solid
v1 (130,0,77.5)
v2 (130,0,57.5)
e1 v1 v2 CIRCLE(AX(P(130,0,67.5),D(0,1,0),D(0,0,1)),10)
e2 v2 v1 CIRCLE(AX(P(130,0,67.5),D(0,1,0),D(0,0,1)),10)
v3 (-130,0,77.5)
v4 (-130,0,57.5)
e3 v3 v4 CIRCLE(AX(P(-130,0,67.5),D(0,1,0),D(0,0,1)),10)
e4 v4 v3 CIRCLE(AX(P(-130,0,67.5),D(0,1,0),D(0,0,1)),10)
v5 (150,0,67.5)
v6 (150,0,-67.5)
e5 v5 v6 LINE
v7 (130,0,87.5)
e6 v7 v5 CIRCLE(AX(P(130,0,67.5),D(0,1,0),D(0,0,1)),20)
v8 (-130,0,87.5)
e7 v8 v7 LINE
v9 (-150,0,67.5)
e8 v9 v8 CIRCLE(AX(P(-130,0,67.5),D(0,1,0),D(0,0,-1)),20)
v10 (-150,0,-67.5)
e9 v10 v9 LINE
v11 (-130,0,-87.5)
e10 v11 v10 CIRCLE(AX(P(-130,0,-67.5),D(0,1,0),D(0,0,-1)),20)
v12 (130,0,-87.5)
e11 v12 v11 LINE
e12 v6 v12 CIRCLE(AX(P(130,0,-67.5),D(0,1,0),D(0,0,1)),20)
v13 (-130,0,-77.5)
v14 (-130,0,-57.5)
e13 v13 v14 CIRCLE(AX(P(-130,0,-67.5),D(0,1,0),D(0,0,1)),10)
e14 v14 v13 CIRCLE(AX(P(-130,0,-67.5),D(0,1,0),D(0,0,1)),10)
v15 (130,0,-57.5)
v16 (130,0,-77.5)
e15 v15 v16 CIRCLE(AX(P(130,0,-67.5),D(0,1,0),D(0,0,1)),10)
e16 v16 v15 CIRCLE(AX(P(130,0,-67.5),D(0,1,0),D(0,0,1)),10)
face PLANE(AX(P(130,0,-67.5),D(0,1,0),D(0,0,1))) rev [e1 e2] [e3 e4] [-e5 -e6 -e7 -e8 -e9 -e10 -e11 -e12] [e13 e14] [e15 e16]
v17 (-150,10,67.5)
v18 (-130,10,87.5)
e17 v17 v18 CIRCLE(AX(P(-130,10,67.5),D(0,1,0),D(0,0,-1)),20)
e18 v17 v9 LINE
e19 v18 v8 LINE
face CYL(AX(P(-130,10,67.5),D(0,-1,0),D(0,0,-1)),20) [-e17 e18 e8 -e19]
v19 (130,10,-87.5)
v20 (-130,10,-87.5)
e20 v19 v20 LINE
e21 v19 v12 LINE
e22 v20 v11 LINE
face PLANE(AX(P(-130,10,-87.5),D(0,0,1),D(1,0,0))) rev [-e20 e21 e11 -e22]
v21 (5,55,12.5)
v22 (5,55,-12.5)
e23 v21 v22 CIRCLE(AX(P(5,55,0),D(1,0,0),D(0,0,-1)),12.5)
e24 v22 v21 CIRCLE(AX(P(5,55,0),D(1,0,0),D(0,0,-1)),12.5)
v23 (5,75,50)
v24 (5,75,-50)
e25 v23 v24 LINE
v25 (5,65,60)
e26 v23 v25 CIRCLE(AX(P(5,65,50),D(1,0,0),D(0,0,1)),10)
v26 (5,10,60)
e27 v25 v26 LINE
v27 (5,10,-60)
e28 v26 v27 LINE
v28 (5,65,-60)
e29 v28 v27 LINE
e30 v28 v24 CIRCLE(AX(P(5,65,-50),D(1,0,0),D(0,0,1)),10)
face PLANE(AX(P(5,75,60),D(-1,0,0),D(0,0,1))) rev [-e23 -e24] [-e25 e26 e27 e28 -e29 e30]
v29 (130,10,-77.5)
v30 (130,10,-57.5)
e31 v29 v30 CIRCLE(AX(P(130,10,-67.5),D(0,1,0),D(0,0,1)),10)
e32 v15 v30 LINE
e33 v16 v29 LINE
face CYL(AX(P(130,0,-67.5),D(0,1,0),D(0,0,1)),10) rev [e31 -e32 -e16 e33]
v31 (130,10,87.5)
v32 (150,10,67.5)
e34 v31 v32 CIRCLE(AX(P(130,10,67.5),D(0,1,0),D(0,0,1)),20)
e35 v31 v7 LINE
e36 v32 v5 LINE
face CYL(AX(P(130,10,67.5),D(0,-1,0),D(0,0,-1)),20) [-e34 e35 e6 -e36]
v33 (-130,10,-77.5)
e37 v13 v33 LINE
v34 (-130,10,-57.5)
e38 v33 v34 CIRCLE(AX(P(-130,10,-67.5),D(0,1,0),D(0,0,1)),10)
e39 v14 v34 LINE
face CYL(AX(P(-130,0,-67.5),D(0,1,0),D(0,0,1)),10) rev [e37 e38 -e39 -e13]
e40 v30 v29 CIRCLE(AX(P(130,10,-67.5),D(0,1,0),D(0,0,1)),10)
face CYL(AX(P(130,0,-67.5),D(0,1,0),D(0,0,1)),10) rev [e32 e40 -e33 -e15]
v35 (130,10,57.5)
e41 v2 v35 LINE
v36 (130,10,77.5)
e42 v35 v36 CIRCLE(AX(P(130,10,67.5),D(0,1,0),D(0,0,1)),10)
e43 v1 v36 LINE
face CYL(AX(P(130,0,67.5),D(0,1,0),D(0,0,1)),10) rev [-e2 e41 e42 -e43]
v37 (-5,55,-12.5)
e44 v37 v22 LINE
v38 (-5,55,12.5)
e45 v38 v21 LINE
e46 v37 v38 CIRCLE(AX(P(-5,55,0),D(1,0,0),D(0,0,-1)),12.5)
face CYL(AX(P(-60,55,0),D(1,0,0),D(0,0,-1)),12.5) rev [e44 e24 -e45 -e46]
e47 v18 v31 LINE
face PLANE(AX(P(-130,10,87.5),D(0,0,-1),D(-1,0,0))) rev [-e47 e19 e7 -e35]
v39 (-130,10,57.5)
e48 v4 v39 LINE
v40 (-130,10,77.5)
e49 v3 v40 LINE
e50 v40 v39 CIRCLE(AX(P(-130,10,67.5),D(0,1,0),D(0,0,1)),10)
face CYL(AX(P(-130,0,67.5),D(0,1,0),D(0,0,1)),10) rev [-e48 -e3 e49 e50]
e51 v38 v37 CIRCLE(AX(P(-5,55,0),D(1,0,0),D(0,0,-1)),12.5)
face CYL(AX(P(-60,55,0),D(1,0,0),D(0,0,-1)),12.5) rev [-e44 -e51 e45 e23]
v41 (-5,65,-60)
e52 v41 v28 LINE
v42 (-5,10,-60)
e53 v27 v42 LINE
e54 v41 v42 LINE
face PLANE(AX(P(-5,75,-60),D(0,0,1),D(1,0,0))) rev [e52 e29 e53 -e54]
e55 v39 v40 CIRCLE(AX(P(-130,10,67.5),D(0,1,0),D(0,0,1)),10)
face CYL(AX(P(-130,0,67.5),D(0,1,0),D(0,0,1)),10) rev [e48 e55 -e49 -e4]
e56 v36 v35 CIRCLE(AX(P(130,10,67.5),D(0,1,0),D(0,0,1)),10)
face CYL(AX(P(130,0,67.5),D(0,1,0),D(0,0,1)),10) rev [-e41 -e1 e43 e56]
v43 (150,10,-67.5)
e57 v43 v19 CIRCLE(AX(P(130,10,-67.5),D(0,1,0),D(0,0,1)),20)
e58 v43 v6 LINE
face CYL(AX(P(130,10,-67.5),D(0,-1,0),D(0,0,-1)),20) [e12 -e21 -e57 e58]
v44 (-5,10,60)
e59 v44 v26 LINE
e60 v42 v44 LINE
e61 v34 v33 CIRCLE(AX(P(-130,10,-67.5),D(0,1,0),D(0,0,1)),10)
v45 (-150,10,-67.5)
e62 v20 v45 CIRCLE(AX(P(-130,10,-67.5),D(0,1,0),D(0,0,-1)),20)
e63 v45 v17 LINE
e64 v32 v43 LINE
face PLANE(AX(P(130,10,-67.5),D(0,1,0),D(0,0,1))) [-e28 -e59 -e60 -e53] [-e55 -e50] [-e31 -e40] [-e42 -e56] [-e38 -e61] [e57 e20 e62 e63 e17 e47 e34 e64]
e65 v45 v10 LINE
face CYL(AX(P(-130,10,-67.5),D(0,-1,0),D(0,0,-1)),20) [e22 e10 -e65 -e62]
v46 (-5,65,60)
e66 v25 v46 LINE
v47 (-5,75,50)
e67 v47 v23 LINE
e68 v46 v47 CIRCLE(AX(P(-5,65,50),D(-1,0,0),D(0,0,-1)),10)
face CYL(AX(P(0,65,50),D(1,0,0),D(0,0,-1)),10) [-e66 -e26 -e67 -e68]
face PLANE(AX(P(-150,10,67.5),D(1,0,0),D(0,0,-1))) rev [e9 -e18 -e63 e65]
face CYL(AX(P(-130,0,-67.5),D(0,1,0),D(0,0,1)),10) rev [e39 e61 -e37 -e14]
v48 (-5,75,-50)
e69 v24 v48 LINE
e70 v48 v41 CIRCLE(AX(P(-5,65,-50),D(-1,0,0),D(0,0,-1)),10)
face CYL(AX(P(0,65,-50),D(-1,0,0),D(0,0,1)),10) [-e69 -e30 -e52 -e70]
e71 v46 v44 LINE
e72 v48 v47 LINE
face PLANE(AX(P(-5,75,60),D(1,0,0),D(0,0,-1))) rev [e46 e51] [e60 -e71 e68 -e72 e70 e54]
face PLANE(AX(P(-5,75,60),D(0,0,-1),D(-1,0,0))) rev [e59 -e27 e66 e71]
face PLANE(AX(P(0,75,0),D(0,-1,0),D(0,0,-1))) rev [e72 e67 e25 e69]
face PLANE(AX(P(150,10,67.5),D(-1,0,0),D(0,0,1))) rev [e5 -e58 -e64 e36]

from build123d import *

# Parameters (mm, degrees)
BASE_PLATE_DEPTH          = 10
MOUNTING_HOLES_SKETCH_R   = 10
MOUNTING_HOLES_4X_DEPTH   = 10
UPRIGHT_TAB_SKETCH_W      = 10
UPRIGHT_TAB_SKETCH_H      = 120
UPRIGHT_TAB_DEPTH         = 65
TAB_CORNER_FILLET_1_R10_R = 10
TAB_CORNER_FILLET_2_R10_R = 10
TAB_HOLE_SKETCH_R         = 12.5
TAB_HOLE_DEPTH            = 65


with BuildPart() as part:
    # Base Plate Sketch → Base Plate (new body)
    with BuildSketch(Plane(origin=(0, 0, 0), x_dir=(1, 0, 0), z_dir=(0, 1, 0))):
        with BuildLine():
            Line((-130, -87.5), (130, -87.5))
            ThreePointArc((130, -87.5), (144.142135624, -81.642135624), (150, -67.5))
            Line((150, -67.5), (150, 67.5))
            ThreePointArc((150, 67.5), (144.142135624, 81.642135624), (130, 87.5))
            Line((130, 87.5), (-130, 87.5))
            ThreePointArc((-130, 87.5), (-144.142135624, 81.642135624), (-150, 67.5))
            Line((-150, 67.5), (-150, -67.5))
            ThreePointArc((-150, -67.5), (-144.142135624, -81.642135624), (-130, -87.5))
        make_face()
    extrude(amount=BASE_PLATE_DEPTH)

    # Mounting Holes Sketch → Mounting Holes 4x (cut)
    with BuildSketch(Plane(origin=(0, 10, 0), x_dir=(1, 0, 0), z_dir=(0, 1, 0))):
        with Locations(Location((130, 67.5, 0), (0, 0, 270))):
            Circle(MOUNTING_HOLES_SKETCH_R)
        with Locations(Location((130, -67.5, 0), (0, 0, 270))):
            Circle(MOUNTING_HOLES_SKETCH_R)
        with Locations(Location((-130, 67.5, 0), (0, 0, 270))):
            Circle(MOUNTING_HOLES_SKETCH_R)
        with Locations(Location((-130, -67.5, 0), (0, 0, 270))):
            Circle(MOUNTING_HOLES_SKETCH_R)
    extrude(amount=-MOUNTING_HOLES_4X_DEPTH, mode=Mode.SUBTRACT)

    # Upright Tab Sketch → Upright Tab (add)
    with BuildSketch(Plane(origin=(0, 10, 0), x_dir=(1, 0, 0), z_dir=(0, 1, 0))):
        Rectangle(UPRIGHT_TAB_SKETCH_W, UPRIGHT_TAB_SKETCH_H)
    extrude(amount=UPRIGHT_TAB_DEPTH)

    # Tab Corner Fillet 1 R10
    tab_corner_fillet_1_r10_edges = [part.edges().sort_by_distance(p)[0] for p in [
        (0, 75, 60),
    ]]
    fillet(tab_corner_fillet_1_r10_edges, radius=TAB_CORNER_FILLET_1_R10_R)

    # Tab Corner Fillet 2 R10
    tab_corner_fillet_2_r10_edges = [part.edges().sort_by_distance(p)[0] for p in [
        (0, 75, -60),
    ]]
    fillet(tab_corner_fillet_2_r10_edges, radius=TAB_CORNER_FILLET_2_R10_R)

    # Tab Hole Sketch → Tab Hole (cut)
    with BuildSketch(Plane(origin=(5, 0, 0), x_dir=(0, 0, -1), z_dir=(1, 0, 0))):
        with Locations((0, 55)):
            Circle(TAB_HOLE_SKETCH_R)
    extrude(amount=-TAB_HOLE_DEPTH, mode=Mode.SUBTRACT)


solid = part.part
